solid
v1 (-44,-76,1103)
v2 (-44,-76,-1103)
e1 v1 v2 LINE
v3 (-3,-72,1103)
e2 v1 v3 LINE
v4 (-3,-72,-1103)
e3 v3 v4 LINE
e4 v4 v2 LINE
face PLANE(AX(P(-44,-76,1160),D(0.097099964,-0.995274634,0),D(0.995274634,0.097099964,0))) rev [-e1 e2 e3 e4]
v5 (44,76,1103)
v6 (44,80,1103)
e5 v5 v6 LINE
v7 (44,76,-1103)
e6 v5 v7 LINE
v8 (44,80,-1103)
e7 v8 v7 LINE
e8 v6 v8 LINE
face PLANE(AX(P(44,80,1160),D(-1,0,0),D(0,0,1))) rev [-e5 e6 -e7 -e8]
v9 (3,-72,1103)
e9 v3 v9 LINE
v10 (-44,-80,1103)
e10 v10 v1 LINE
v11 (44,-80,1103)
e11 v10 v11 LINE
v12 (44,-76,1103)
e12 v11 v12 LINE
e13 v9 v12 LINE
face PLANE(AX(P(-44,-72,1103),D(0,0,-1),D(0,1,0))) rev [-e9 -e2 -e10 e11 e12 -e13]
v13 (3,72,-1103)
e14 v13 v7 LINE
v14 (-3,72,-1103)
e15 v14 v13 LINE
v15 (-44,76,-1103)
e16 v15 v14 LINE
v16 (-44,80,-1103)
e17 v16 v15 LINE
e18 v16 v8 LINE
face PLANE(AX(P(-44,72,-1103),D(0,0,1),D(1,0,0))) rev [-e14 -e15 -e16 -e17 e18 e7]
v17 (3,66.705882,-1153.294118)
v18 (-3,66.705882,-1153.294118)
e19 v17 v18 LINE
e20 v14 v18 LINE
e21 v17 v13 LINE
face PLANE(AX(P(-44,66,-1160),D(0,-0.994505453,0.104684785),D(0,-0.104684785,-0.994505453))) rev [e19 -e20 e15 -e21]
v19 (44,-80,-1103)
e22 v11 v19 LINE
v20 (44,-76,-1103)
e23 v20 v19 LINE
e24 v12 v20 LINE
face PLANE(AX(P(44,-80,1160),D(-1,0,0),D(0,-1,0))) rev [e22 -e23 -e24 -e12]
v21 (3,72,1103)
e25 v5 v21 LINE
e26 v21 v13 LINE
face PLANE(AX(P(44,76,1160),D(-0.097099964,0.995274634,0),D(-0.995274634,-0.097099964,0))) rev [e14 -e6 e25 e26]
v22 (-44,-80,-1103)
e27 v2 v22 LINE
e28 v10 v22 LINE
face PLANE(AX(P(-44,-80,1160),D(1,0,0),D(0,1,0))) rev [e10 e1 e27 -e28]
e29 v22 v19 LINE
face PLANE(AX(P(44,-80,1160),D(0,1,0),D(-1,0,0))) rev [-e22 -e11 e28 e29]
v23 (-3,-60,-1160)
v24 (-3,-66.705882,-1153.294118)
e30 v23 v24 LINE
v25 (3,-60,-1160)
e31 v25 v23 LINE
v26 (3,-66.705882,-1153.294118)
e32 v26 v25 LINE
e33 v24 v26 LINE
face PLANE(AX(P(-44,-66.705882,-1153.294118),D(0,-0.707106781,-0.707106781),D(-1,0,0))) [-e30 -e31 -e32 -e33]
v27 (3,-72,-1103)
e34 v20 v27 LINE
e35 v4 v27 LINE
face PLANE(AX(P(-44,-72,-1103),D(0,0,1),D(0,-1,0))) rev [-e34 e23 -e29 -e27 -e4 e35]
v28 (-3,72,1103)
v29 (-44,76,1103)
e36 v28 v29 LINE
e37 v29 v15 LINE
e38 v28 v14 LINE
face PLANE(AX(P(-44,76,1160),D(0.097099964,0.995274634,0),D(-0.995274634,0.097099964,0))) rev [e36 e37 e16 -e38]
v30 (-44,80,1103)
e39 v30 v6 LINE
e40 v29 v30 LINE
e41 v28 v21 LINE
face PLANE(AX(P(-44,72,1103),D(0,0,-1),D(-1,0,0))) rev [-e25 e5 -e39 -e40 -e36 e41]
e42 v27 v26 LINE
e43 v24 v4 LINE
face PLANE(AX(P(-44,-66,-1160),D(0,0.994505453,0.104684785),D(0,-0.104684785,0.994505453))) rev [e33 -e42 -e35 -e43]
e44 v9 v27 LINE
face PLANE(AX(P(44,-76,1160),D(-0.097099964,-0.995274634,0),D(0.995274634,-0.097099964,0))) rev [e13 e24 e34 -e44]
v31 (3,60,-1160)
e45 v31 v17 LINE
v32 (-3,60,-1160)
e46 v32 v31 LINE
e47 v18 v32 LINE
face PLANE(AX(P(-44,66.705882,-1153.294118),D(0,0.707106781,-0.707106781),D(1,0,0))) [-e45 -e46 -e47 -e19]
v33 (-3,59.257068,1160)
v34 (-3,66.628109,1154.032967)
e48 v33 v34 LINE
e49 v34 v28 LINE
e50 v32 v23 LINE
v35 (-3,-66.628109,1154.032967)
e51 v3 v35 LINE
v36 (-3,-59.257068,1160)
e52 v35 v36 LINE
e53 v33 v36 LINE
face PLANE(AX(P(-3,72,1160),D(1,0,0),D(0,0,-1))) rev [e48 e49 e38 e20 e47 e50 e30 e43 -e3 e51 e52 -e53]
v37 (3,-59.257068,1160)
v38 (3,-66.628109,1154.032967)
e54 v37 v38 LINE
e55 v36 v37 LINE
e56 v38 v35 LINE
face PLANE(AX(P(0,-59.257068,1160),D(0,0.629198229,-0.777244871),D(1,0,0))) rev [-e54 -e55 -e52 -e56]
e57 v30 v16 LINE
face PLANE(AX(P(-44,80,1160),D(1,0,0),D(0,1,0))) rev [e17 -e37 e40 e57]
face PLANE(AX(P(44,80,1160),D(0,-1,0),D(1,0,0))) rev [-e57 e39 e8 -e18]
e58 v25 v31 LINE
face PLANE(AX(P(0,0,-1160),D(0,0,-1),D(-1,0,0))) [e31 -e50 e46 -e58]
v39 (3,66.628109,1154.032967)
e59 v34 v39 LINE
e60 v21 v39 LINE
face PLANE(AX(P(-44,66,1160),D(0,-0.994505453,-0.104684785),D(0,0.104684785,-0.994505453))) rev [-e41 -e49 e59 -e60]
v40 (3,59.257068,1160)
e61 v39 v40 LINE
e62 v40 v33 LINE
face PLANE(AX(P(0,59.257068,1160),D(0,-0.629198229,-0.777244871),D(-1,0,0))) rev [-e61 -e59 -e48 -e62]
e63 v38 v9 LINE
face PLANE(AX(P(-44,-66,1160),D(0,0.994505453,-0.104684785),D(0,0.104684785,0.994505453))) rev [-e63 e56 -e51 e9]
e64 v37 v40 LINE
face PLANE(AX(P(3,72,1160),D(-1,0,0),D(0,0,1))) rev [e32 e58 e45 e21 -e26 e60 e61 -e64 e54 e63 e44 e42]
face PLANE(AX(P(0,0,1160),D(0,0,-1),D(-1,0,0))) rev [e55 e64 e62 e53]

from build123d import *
from OCP.BRepFilletAPI import BRepFilletAPI_MakeChamfer

# Parameters (mm, degrees)
EXTRUDE_1_DEPTH          = 1160
CUT_EXTRUDE_1_DEPTH      = 1164.587555795
CUT_EXTRUDE_1_DEPTH_BACK = 1164.587555795
CHAMFER_1_SIZE           = 6
CHAMFER_1_SIZE2          = 6.742931709


with BuildPart() as part:
    # 草图1 → 凸台-拉伸1 (new, symmetric)
    with BuildSketch(Plane.XY):
        Polygon((44, 80), (-44, 80), (-44, 76), (-3, 72), (-3, -72), (-44, -76), (-44, -80), (44, -80), (44, -76), (3, -72), (3, 72), (44, 76), align=None)
    extrude(amount=EXTRUDE_1_DEPTH, both=True)

    # 草图3 → 切除-拉伸1 (cut, two sides: drawn at the far end of the back side and taken through both)
    with BuildSketch(Plane(origin=(0, 0, 0), x_dir=(0, 0, -1), z_dir=(1, 0, 0)).offset(-CUT_EXTRUDE_1_DEPTH_BACK)):
        Polygon((-1160, 66), (-1103, 72), (-1103, 80), (-1160, 80), align=None)
        Polygon((1160, 80), (1160, 66), (1103, 72), (1103, 80), align=None)
        Polygon((1160, -66), (1103, -72), (1103, -80), (1160, -80), align=None)
        Polygon((-1160, -80), (-1160, -66), (-1103, -72), (-1103, -80), align=None)
    extrude(amount=CUT_EXTRUDE_1_DEPTH + CUT_EXTRUDE_1_DEPTH_BACK, mode=Mode.SUBTRACT)

    # 倒角1: one chamfer whose edges measure the first distance from different faces: ONE call of the kernel's chamfer builder (chamfer() names one face for all edges)
    chamfer_1_edges_1 = [part.edges().sort_by_distance(p)[0] for p in [
        (0, 66, -1160),
        (0, -66, -1160),
    ]]
    chamfer_1_side_1 = [part.faces().sort_by_distance(p)[0] for p in [
        (0, 0, -1160),
    ]]
    chamfer_1_edges_2 = [part.edges().sort_by_distance(p)[0] for p in [
        (0, 66, 1160),
    ]]
    chamfer_1_side_2 = [part.faces().sort_by_distance(p)[0] for p in [
        (0, 69, 1131.5),
    ]]
    chamfer_1_edges_3 = [part.edges().sort_by_distance(p)[0] for p in [
        (0, -66, 1160),
    ]]
    chamfer_1_side_3 = [part.faces().sort_by_distance(p)[0] for p in [
        (0, -69, 1131.5),
    ]]
    chamfer_1 = BRepFilletAPI_MakeChamfer(part.part.solid().wrapped)
    for e in chamfer_1_edges_1:
        chamfer_1.Add(CHAMFER_1_SIZE, CHAMFER_1_SIZE2, e.wrapped, chamfer_1_side_1[0].wrapped)  # the first distance lies on this face
    for e in chamfer_1_edges_2:
        chamfer_1.Add(CHAMFER_1_SIZE, CHAMFER_1_SIZE2, e.wrapped, chamfer_1_side_2[0].wrapped)  # the first distance lies on this face
    for e in chamfer_1_edges_3:
        chamfer_1.Add(CHAMFER_1_SIZE, CHAMFER_1_SIZE2, e.wrapped, chamfer_1_side_3[0].wrapped)  # the first distance lies on this face
    add(Compound.cast(chamfer_1.Shape()), mode=Mode.REPLACE)


solid = part.part
